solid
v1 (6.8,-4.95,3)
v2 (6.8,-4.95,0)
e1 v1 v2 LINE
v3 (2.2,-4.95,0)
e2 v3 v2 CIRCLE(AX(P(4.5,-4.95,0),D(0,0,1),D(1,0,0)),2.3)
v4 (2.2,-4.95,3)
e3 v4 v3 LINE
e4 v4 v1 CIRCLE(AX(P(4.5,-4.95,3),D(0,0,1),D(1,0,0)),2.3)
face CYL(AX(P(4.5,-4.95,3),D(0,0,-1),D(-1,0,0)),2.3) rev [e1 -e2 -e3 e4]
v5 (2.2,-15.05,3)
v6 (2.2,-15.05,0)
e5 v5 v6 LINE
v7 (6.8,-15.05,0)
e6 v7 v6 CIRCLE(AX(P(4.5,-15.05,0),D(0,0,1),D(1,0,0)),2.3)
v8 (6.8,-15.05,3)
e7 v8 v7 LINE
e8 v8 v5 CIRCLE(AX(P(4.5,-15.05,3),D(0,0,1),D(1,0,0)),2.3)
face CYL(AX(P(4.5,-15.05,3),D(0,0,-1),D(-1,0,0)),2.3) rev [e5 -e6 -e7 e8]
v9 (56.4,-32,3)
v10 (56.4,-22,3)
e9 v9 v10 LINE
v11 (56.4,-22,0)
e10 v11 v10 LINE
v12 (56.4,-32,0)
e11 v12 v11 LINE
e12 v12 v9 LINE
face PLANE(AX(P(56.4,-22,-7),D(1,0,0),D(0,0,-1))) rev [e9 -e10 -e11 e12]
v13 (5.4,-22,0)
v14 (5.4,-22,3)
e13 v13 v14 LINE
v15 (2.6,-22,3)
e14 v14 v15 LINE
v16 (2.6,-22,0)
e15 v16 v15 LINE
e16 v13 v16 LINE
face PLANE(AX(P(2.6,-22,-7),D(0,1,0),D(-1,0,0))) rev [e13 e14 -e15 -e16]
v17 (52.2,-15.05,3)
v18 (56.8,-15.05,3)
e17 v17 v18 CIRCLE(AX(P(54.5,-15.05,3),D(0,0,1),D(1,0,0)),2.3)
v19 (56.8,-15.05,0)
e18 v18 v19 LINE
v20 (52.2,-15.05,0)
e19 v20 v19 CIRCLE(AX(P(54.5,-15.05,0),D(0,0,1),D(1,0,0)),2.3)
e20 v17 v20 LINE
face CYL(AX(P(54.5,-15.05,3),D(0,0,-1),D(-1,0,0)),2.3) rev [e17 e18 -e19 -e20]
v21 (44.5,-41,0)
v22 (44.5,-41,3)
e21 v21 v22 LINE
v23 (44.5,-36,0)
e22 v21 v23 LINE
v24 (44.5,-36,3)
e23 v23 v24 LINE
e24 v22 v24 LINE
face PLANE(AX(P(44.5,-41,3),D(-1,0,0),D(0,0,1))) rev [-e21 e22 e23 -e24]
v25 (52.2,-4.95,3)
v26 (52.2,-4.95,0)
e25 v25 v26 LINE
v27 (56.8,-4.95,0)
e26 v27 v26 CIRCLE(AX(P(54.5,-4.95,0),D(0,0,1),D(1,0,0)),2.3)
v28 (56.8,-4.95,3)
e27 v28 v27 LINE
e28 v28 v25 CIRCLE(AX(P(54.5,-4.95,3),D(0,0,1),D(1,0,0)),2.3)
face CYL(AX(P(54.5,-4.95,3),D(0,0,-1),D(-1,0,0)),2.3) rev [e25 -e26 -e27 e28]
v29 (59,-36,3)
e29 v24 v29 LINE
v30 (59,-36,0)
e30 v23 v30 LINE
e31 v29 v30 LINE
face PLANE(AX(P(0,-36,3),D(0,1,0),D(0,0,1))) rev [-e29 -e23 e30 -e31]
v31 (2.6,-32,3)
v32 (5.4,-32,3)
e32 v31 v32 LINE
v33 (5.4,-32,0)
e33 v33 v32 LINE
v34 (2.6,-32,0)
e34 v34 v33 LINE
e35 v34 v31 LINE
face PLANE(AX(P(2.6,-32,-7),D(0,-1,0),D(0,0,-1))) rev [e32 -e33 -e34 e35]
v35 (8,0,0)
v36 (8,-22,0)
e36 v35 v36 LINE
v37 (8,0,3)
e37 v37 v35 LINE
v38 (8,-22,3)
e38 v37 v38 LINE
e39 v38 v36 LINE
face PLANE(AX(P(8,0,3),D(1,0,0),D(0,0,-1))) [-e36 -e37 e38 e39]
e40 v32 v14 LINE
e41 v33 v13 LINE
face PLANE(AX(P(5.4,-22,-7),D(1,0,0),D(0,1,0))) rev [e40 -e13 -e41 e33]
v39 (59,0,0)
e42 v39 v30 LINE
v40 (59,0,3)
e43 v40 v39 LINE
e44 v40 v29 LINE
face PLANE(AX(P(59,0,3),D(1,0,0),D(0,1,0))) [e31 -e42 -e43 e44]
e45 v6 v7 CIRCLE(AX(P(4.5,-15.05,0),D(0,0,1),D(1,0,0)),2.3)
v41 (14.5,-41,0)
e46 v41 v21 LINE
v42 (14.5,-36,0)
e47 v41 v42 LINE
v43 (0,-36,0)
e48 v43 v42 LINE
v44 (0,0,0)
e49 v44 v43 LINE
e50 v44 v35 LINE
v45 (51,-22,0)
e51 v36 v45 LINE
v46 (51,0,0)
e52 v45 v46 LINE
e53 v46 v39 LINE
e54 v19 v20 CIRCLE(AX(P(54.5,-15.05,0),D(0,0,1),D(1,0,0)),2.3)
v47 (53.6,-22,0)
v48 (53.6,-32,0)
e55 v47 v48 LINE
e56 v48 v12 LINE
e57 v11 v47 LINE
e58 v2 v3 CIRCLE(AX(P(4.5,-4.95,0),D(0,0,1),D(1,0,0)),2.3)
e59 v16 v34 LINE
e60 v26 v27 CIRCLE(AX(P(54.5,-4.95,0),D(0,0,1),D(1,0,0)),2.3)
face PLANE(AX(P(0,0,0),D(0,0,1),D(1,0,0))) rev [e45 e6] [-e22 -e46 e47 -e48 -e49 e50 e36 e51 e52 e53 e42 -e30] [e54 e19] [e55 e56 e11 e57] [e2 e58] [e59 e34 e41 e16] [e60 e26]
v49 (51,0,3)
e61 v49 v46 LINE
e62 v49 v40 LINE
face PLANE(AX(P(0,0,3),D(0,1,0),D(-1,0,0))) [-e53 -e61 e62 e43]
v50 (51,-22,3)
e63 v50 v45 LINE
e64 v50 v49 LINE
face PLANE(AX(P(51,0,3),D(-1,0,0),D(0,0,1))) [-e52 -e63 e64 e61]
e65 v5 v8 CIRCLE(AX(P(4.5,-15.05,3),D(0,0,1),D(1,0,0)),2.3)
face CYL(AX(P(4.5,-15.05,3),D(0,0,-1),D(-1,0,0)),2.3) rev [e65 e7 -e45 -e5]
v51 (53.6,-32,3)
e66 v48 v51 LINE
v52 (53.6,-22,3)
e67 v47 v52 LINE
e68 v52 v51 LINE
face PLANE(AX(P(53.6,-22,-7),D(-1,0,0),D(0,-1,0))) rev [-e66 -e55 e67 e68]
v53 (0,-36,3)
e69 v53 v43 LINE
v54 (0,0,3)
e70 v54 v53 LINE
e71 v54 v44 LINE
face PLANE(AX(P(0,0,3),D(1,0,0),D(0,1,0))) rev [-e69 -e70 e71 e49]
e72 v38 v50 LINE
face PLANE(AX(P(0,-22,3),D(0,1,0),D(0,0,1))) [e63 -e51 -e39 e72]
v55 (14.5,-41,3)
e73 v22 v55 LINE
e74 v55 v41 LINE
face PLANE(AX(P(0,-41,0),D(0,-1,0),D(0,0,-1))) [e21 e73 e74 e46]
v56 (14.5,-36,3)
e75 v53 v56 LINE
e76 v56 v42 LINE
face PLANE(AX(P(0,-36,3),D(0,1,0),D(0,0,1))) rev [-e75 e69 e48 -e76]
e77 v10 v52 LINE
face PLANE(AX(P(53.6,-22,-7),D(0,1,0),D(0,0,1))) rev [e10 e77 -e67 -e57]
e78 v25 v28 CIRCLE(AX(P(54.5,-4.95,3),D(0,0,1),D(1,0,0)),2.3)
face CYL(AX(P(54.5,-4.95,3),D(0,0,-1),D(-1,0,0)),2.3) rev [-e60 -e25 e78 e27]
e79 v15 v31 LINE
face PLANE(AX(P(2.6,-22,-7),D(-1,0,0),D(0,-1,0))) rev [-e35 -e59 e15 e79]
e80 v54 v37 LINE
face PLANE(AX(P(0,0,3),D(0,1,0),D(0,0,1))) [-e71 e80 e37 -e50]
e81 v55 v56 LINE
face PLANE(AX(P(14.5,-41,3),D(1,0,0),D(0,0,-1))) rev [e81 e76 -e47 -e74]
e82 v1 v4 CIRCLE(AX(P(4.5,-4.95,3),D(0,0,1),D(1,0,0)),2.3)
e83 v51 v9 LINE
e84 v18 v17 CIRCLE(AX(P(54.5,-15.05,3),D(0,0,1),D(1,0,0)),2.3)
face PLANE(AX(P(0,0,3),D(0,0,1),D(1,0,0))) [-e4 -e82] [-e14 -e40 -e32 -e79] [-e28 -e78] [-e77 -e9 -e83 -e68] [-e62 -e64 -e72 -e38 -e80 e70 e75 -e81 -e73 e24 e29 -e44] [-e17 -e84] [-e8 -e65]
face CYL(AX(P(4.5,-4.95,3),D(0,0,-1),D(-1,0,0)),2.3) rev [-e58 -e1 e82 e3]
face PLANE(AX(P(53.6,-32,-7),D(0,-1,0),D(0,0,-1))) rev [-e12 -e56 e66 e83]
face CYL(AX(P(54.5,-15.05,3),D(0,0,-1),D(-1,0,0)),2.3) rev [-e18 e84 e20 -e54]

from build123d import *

# Parameters (mm, degrees)
SKETCH1_R           = 2.3
BOSS_EXTRUDE1_DEPTH = 3
SKETCH3_W           = 2.8
SKETCH3_H           = 10
CUT_EXTRUDE1_DEPTH  = 10
SKETCH4_W           = 30
SKETCH4_H           = 3
BOSS_EXTRUDE2_DEPTH = 5


with BuildPart() as part:
    # Sketch1 → Boss-Extrude1 (new body)
    with BuildSketch(Plane.XY):
        Polygon((0, 0), (8, 0), (8, -22), (51, -22), (51, 0), (59, 0), (59, -36), (0, -36), align=None)
        with Locations((4.5, -15.05)):
            Circle(SKETCH1_R, mode=Mode.SUBTRACT)
        with Locations((4.5, -4.95)):
            Circle(SKETCH1_R, mode=Mode.SUBTRACT)
        with Locations((54.5, -4.95)):
            Circle(SKETCH1_R, mode=Mode.SUBTRACT)
        with Locations((54.5, -15.05)):
            Circle(SKETCH1_R, mode=Mode.SUBTRACT)
    extrude(amount=BOSS_EXTRUDE1_DEPTH)

    # Sketch3 → Cut-Extrude1 (cut)
    with BuildSketch(Plane.XY.offset(3)):
        with Locations((4, -27)):
            Rectangle(SKETCH3_W, SKETCH3_H)
        with Locations((55, -27)):
            Rectangle(SKETCH3_W, SKETCH3_H)
    extrude(amount=-CUT_EXTRUDE1_DEPTH, mode=Mode.SUBTRACT)

    # Sketch4 → Boss-Extrude2 (add)
    with BuildSketch(Plane.XZ.offset(36)):
        with Locations((29.5, 1.5)):
            Rectangle(SKETCH4_W, SKETCH4_H)
    extrude(amount=BOSS_EXTRUDE2_DEPTH)


solid = part.part
